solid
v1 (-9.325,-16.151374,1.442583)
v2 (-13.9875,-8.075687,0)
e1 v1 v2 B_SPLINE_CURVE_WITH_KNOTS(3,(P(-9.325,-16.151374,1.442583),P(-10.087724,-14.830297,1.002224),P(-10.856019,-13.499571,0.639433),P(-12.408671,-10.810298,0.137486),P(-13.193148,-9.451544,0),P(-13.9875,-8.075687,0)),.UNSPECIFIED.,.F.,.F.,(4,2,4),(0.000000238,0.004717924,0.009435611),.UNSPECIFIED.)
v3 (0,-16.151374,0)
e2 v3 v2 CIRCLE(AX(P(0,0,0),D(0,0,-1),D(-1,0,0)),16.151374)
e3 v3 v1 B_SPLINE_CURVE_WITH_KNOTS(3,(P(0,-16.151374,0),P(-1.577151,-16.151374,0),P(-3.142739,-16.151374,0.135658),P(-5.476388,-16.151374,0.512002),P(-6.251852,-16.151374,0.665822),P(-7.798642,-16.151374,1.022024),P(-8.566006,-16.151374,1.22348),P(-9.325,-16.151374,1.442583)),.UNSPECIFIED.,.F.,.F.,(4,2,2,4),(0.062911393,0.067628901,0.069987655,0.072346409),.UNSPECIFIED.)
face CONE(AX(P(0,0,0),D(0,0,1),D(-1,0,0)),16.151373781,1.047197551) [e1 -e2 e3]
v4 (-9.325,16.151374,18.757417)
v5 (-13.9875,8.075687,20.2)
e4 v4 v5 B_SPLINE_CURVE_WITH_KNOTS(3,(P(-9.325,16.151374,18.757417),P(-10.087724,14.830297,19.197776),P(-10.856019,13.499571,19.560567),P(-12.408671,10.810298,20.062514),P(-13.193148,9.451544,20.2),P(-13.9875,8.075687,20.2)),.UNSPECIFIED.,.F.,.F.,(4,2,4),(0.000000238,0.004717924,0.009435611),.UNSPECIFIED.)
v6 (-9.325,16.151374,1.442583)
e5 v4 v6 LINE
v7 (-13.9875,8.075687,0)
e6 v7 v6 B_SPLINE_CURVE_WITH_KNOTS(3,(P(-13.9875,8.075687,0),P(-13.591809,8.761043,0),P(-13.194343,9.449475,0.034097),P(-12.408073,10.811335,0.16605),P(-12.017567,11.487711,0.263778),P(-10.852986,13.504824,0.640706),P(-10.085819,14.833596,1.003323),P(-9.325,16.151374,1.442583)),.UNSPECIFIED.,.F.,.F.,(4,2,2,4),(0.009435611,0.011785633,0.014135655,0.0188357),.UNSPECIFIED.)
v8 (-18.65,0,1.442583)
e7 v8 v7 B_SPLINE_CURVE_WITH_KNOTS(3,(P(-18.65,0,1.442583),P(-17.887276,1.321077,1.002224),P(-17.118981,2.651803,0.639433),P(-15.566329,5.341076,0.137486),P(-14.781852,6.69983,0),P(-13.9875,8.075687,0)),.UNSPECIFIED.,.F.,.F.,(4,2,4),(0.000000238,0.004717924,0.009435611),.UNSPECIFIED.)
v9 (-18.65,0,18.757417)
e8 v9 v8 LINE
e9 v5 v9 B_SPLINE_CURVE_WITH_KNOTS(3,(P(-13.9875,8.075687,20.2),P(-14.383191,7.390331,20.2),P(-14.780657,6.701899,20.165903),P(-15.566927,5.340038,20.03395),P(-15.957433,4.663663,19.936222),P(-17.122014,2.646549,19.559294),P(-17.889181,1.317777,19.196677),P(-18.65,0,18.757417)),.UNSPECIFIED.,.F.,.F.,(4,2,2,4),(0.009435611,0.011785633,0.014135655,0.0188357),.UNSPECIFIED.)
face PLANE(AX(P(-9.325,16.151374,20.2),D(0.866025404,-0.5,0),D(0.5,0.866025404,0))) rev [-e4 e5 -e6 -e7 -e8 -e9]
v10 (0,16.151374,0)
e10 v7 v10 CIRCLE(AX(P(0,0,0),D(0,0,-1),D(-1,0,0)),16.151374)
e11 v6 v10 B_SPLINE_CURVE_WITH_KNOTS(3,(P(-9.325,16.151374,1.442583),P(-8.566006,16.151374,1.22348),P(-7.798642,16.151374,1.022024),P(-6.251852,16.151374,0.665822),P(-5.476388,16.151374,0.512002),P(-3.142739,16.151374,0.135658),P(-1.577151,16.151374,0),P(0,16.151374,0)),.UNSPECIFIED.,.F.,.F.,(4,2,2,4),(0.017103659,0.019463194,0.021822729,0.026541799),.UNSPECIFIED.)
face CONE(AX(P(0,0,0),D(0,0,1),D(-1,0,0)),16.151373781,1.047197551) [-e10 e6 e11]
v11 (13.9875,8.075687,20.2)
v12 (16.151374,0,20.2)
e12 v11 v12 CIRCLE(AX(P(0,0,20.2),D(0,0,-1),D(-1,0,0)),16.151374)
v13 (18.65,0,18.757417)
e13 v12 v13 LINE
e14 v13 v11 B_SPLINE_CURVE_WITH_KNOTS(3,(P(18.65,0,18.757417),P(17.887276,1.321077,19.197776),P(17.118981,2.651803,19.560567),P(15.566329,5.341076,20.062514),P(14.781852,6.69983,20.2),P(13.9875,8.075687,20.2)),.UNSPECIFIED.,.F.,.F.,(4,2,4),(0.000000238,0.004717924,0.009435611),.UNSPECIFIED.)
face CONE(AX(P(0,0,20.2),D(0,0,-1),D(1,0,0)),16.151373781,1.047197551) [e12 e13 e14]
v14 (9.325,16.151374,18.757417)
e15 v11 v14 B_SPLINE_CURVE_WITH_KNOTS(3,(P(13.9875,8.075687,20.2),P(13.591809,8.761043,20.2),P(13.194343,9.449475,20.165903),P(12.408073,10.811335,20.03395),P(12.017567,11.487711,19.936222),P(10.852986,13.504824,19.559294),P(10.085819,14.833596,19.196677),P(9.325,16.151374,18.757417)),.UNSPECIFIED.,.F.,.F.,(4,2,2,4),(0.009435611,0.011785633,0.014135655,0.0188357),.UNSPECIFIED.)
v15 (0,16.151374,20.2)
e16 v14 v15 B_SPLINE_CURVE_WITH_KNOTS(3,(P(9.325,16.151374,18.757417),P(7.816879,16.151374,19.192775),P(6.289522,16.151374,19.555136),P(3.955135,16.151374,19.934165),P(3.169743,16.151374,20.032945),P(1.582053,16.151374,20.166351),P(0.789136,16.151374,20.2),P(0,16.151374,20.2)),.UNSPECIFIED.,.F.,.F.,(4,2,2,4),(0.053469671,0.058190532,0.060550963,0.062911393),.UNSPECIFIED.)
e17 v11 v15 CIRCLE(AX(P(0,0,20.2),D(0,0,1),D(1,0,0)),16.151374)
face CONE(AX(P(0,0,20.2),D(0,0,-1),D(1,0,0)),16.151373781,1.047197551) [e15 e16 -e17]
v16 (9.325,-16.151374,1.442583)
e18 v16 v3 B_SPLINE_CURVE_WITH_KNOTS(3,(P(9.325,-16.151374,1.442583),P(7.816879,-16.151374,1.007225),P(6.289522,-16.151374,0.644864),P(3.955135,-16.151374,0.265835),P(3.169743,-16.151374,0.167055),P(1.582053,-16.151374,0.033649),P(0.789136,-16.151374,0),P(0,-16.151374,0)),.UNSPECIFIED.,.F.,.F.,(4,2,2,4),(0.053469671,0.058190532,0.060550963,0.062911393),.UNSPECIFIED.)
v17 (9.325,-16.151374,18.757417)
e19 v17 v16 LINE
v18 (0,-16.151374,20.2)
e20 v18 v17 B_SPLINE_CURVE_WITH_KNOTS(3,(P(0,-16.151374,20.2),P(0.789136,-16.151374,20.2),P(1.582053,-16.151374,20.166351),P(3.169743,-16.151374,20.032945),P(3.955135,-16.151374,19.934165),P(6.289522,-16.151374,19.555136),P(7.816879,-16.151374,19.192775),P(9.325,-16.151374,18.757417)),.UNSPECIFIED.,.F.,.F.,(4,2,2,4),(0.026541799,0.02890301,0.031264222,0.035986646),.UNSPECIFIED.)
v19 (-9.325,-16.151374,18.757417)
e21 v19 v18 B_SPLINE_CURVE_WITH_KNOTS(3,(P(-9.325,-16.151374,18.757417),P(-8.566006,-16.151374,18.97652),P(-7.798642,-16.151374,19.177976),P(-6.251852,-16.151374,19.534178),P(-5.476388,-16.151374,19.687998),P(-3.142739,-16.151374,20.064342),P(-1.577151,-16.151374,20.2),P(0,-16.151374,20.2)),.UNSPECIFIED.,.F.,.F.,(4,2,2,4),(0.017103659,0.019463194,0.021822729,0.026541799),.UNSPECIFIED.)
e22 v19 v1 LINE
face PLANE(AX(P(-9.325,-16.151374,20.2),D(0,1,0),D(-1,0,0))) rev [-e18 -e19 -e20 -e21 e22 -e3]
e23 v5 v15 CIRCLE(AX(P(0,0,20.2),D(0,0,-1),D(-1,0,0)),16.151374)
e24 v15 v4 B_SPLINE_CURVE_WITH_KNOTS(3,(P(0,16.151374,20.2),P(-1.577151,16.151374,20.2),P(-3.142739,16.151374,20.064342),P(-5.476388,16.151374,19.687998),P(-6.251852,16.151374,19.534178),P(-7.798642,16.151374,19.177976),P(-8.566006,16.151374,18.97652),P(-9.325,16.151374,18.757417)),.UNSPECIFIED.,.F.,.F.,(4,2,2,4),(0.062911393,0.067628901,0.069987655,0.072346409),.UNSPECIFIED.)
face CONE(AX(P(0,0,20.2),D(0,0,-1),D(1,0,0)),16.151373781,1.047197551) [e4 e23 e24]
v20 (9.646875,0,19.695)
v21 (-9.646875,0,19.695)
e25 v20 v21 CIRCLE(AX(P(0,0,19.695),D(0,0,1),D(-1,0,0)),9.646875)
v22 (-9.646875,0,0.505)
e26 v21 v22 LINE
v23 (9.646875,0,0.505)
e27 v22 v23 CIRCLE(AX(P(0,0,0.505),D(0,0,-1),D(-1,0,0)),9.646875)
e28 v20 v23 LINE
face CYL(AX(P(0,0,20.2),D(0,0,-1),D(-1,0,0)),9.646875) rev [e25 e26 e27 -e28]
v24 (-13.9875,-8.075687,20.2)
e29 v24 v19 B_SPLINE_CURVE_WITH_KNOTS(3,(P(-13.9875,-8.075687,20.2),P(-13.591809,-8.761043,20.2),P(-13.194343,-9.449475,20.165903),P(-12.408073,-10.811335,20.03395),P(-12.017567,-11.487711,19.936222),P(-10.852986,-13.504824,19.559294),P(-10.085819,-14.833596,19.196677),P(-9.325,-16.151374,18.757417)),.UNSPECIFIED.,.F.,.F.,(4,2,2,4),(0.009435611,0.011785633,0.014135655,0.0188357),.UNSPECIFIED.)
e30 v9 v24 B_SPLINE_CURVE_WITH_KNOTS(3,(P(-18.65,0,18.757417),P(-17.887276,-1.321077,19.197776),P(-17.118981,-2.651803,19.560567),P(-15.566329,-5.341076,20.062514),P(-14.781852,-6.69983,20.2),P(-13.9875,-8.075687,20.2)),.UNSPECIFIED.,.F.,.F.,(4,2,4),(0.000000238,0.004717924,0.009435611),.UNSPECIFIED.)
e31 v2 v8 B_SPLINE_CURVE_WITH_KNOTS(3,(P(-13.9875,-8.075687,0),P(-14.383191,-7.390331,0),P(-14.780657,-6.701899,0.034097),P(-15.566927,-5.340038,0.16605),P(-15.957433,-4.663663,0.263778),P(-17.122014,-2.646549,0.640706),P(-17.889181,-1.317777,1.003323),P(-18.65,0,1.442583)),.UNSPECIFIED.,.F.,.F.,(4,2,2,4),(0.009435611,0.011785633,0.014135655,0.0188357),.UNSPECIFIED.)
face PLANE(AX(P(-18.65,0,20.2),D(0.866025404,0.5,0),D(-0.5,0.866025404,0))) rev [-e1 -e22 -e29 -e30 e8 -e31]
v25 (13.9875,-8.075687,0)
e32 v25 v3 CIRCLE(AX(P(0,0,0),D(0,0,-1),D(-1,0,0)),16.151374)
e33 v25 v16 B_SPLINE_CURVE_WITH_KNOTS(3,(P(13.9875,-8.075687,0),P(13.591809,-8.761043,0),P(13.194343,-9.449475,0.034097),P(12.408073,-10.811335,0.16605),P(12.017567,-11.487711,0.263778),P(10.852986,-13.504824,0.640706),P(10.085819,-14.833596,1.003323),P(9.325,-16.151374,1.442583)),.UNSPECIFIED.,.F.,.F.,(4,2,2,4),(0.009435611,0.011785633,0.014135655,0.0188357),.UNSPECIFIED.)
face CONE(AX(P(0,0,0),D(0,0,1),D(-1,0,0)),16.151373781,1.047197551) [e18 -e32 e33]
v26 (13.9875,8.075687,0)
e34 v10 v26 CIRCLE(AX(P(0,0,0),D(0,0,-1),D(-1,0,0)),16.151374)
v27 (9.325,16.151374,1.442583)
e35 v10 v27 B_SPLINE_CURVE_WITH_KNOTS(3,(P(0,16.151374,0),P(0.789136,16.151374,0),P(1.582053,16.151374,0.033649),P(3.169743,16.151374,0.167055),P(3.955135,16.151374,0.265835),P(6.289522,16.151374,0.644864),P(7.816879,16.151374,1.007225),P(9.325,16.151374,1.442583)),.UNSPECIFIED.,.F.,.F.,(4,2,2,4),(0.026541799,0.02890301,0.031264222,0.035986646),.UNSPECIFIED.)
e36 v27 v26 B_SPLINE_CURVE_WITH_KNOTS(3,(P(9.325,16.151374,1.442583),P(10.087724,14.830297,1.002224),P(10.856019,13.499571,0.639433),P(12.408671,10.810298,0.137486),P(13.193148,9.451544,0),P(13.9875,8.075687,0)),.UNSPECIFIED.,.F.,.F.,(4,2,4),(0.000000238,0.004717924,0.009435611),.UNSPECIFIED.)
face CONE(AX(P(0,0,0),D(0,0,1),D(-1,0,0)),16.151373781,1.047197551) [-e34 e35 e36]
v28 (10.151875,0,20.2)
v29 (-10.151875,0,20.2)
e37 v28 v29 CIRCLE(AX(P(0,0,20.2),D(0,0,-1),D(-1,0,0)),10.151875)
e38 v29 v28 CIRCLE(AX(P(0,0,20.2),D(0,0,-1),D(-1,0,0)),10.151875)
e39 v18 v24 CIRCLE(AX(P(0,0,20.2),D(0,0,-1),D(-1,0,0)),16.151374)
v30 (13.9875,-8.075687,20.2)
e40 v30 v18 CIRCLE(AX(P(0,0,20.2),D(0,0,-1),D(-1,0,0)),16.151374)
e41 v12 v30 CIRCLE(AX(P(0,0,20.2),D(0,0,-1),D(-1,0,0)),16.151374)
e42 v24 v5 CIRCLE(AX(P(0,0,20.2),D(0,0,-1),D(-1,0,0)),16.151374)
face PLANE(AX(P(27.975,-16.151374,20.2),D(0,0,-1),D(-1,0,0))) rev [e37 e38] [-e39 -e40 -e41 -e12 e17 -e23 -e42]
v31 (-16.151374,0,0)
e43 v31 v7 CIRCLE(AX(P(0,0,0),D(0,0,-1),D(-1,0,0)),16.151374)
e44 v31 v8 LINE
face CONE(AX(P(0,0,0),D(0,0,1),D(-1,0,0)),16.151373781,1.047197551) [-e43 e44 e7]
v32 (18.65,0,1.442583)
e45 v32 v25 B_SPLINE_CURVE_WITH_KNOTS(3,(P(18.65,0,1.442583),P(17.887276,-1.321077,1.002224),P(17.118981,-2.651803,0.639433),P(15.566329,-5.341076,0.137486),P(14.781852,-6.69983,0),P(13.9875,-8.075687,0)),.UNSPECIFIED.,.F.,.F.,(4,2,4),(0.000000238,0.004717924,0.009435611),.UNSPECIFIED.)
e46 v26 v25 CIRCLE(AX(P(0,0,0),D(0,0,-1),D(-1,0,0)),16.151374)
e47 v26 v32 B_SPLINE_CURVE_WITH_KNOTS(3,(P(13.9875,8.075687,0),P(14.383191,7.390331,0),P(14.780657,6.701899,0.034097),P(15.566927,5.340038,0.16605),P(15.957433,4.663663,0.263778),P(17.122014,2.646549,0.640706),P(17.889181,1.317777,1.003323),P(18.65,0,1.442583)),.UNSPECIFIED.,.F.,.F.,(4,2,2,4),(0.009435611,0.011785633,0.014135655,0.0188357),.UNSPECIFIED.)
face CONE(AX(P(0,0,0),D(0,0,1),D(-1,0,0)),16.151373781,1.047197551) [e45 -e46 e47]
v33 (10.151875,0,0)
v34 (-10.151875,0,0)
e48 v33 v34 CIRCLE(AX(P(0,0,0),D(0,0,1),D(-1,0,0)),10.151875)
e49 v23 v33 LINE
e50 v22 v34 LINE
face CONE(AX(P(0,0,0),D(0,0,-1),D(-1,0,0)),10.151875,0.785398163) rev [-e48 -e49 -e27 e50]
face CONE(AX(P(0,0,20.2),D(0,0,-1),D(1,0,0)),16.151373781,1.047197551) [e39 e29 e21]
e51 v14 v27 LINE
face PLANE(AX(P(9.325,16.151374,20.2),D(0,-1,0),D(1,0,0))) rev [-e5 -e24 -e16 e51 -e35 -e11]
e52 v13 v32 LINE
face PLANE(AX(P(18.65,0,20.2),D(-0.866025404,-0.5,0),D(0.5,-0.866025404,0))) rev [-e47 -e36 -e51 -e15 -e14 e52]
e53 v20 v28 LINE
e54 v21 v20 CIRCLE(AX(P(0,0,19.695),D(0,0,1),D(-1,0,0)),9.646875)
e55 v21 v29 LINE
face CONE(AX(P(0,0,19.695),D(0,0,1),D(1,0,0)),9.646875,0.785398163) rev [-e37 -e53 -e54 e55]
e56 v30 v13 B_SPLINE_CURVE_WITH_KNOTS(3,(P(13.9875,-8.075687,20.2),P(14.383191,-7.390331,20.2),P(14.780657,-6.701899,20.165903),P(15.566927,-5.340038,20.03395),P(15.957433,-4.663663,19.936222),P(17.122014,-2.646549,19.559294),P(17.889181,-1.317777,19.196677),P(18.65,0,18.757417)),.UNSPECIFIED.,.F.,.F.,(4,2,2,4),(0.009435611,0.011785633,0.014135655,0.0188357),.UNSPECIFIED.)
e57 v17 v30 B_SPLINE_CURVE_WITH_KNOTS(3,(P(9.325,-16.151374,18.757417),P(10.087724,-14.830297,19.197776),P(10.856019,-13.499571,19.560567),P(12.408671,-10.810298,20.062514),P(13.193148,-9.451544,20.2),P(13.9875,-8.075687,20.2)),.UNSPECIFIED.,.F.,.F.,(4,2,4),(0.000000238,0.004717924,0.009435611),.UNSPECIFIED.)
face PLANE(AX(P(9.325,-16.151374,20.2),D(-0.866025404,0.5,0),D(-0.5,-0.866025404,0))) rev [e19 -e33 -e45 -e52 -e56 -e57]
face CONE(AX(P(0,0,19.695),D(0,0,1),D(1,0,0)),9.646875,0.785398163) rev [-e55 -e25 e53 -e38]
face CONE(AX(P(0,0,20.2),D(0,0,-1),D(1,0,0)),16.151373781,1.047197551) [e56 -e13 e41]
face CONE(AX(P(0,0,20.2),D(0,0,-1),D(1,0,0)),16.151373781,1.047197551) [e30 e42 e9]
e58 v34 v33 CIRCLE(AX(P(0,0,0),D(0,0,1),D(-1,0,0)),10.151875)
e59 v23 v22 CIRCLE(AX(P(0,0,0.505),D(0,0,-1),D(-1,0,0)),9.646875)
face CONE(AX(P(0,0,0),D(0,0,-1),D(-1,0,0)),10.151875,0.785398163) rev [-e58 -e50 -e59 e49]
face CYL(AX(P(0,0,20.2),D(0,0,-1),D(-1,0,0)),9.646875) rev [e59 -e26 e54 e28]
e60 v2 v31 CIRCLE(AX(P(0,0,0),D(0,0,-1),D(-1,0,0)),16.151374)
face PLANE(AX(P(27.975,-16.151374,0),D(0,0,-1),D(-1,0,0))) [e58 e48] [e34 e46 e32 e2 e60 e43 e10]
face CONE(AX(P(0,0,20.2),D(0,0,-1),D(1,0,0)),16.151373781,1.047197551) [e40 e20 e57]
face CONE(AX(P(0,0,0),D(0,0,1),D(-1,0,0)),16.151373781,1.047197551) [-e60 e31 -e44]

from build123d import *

# Parameters (mm, degrees)
SKETCH_1_R          = 9.646875
EXTRUDE_483_DEPTH   = 20.2
SKETCH_2_OUTSIDE_W  = 163.884
SKETCH_2_OUTSIDE_H  = 158.886
SKETCH_2_OUTSIDE_R  = 16.151373781
CUT_EXTRUDE_1_DEPTH = 32.886194113
CUT_EXTRUDE_1_DRAFT = -60
SKETCH_3_OUTSIDE_W  = 163.884
SKETCH_3_OUTSIDE_H  = 158.886
SKETCH_3_OUTSIDE_R  = 16.151373781
CUT_EXTRUDE_2_DEPTH = 32.886194113
CUT_EXTRUDE_2_DRAFT = -60
CHAMFER_1_SIZE      = 0.505


with BuildPart() as part:
    # 草图1 → Extrude 483 (new body)
    with BuildSketch(Plane.XY):
        Polygon((9.325, 16.151373781), (-9.325, 16.151373781), (-18.65, 0), (-9.325, -16.151373781), (9.325, -16.151373781), (18.65, 0), align=None)
        Circle(SKETCH_1_R, mode=Mode.SUBTRACT)
    extrude(amount=EXTRUDE_483_DEPTH)


with BuildPart() as cut_extrude_1_tool:
    # 草图2 outside → 切除-拉伸1 (with draft: the straight prism first)
    with BuildSketch(Plane(origin=(0, 0, 0), x_dir=(-1, 0, 0), z_dir=(0, 0, -1))):
        Rectangle(SKETCH_2_OUTSIDE_W, SKETCH_2_OUTSIDE_H)
        Circle(SKETCH_2_OUTSIDE_R, mode=Mode.SUBTRACT)
    extrude(amount=-CUT_EXTRUDE_1_DEPTH)
    # 切除-拉伸1: the draft: its side faces are tilted about the plane it starts from
    cut_extrude_1_sides = [cut_extrude_1_tool.faces().sort_by_distance(p)[0] for p in [
        (0, -79.443, 16.443097056),
        (-81.942, 0, 16.443097056),
        (0, 79.443, 16.443097056),
        (81.942, 0, 16.443097056),
        (16.151373781, 0, 16.443097056),
    ]]
    draft(cut_extrude_1_sides, Plane(origin=(0, 0, 0), x_dir=(-1, 0, 0), z_dir=(0, 0, -1)), CUT_EXTRUDE_1_DRAFT)


with BuildPart() as part_1:
    add(part.part)

    # 切除-拉伸1: cut by cut_extrude_1_tool
    add(cut_extrude_1_tool.part, mode=Mode.SUBTRACT)


with BuildPart() as cut_extrude_2_tool:
    # 草图3 outside → 切除-拉伸2 (with draft: the straight prism first)
    with BuildSketch(Plane.XY.offset(20.2)):
        Rectangle(SKETCH_3_OUTSIDE_W, SKETCH_3_OUTSIDE_H)
        Circle(SKETCH_3_OUTSIDE_R, mode=Mode.SUBTRACT)
    extrude(amount=-CUT_EXTRUDE_2_DEPTH)
    # 切除-拉伸2: the draft: its side faces are tilted about the plane it starts from
    cut_extrude_2_sides = [cut_extrude_2_tool.faces().sort_by_distance(p)[0] for p in [
        (0, -79.443, 3.756902944),
        (81.942, 0, 3.756902944),
        (0, 79.443, 3.756902944),
        (-81.942, 0, 3.756902944),
        (-16.151373781, 0, 3.756902944),
    ]]
    draft(cut_extrude_2_sides, Plane.XY.offset(20.2), CUT_EXTRUDE_2_DRAFT)


with BuildPart() as part_2:
    add(part_1.part)

    # 切除-拉伸2: cut by cut_extrude_2_tool
    add(cut_extrude_2_tool.part, mode=Mode.SUBTRACT)

    # 倒角1
    chamfer_1_edges = [part_2.edges().sort_by_distance(p)[0] for p in [
        (-9.646875, 0, 0),
        (-9.646875, 0, 20.2),
    ]]
    chamfer(chamfer_1_edges, length=CHAMFER_1_SIZE)


solid = part_2.part
